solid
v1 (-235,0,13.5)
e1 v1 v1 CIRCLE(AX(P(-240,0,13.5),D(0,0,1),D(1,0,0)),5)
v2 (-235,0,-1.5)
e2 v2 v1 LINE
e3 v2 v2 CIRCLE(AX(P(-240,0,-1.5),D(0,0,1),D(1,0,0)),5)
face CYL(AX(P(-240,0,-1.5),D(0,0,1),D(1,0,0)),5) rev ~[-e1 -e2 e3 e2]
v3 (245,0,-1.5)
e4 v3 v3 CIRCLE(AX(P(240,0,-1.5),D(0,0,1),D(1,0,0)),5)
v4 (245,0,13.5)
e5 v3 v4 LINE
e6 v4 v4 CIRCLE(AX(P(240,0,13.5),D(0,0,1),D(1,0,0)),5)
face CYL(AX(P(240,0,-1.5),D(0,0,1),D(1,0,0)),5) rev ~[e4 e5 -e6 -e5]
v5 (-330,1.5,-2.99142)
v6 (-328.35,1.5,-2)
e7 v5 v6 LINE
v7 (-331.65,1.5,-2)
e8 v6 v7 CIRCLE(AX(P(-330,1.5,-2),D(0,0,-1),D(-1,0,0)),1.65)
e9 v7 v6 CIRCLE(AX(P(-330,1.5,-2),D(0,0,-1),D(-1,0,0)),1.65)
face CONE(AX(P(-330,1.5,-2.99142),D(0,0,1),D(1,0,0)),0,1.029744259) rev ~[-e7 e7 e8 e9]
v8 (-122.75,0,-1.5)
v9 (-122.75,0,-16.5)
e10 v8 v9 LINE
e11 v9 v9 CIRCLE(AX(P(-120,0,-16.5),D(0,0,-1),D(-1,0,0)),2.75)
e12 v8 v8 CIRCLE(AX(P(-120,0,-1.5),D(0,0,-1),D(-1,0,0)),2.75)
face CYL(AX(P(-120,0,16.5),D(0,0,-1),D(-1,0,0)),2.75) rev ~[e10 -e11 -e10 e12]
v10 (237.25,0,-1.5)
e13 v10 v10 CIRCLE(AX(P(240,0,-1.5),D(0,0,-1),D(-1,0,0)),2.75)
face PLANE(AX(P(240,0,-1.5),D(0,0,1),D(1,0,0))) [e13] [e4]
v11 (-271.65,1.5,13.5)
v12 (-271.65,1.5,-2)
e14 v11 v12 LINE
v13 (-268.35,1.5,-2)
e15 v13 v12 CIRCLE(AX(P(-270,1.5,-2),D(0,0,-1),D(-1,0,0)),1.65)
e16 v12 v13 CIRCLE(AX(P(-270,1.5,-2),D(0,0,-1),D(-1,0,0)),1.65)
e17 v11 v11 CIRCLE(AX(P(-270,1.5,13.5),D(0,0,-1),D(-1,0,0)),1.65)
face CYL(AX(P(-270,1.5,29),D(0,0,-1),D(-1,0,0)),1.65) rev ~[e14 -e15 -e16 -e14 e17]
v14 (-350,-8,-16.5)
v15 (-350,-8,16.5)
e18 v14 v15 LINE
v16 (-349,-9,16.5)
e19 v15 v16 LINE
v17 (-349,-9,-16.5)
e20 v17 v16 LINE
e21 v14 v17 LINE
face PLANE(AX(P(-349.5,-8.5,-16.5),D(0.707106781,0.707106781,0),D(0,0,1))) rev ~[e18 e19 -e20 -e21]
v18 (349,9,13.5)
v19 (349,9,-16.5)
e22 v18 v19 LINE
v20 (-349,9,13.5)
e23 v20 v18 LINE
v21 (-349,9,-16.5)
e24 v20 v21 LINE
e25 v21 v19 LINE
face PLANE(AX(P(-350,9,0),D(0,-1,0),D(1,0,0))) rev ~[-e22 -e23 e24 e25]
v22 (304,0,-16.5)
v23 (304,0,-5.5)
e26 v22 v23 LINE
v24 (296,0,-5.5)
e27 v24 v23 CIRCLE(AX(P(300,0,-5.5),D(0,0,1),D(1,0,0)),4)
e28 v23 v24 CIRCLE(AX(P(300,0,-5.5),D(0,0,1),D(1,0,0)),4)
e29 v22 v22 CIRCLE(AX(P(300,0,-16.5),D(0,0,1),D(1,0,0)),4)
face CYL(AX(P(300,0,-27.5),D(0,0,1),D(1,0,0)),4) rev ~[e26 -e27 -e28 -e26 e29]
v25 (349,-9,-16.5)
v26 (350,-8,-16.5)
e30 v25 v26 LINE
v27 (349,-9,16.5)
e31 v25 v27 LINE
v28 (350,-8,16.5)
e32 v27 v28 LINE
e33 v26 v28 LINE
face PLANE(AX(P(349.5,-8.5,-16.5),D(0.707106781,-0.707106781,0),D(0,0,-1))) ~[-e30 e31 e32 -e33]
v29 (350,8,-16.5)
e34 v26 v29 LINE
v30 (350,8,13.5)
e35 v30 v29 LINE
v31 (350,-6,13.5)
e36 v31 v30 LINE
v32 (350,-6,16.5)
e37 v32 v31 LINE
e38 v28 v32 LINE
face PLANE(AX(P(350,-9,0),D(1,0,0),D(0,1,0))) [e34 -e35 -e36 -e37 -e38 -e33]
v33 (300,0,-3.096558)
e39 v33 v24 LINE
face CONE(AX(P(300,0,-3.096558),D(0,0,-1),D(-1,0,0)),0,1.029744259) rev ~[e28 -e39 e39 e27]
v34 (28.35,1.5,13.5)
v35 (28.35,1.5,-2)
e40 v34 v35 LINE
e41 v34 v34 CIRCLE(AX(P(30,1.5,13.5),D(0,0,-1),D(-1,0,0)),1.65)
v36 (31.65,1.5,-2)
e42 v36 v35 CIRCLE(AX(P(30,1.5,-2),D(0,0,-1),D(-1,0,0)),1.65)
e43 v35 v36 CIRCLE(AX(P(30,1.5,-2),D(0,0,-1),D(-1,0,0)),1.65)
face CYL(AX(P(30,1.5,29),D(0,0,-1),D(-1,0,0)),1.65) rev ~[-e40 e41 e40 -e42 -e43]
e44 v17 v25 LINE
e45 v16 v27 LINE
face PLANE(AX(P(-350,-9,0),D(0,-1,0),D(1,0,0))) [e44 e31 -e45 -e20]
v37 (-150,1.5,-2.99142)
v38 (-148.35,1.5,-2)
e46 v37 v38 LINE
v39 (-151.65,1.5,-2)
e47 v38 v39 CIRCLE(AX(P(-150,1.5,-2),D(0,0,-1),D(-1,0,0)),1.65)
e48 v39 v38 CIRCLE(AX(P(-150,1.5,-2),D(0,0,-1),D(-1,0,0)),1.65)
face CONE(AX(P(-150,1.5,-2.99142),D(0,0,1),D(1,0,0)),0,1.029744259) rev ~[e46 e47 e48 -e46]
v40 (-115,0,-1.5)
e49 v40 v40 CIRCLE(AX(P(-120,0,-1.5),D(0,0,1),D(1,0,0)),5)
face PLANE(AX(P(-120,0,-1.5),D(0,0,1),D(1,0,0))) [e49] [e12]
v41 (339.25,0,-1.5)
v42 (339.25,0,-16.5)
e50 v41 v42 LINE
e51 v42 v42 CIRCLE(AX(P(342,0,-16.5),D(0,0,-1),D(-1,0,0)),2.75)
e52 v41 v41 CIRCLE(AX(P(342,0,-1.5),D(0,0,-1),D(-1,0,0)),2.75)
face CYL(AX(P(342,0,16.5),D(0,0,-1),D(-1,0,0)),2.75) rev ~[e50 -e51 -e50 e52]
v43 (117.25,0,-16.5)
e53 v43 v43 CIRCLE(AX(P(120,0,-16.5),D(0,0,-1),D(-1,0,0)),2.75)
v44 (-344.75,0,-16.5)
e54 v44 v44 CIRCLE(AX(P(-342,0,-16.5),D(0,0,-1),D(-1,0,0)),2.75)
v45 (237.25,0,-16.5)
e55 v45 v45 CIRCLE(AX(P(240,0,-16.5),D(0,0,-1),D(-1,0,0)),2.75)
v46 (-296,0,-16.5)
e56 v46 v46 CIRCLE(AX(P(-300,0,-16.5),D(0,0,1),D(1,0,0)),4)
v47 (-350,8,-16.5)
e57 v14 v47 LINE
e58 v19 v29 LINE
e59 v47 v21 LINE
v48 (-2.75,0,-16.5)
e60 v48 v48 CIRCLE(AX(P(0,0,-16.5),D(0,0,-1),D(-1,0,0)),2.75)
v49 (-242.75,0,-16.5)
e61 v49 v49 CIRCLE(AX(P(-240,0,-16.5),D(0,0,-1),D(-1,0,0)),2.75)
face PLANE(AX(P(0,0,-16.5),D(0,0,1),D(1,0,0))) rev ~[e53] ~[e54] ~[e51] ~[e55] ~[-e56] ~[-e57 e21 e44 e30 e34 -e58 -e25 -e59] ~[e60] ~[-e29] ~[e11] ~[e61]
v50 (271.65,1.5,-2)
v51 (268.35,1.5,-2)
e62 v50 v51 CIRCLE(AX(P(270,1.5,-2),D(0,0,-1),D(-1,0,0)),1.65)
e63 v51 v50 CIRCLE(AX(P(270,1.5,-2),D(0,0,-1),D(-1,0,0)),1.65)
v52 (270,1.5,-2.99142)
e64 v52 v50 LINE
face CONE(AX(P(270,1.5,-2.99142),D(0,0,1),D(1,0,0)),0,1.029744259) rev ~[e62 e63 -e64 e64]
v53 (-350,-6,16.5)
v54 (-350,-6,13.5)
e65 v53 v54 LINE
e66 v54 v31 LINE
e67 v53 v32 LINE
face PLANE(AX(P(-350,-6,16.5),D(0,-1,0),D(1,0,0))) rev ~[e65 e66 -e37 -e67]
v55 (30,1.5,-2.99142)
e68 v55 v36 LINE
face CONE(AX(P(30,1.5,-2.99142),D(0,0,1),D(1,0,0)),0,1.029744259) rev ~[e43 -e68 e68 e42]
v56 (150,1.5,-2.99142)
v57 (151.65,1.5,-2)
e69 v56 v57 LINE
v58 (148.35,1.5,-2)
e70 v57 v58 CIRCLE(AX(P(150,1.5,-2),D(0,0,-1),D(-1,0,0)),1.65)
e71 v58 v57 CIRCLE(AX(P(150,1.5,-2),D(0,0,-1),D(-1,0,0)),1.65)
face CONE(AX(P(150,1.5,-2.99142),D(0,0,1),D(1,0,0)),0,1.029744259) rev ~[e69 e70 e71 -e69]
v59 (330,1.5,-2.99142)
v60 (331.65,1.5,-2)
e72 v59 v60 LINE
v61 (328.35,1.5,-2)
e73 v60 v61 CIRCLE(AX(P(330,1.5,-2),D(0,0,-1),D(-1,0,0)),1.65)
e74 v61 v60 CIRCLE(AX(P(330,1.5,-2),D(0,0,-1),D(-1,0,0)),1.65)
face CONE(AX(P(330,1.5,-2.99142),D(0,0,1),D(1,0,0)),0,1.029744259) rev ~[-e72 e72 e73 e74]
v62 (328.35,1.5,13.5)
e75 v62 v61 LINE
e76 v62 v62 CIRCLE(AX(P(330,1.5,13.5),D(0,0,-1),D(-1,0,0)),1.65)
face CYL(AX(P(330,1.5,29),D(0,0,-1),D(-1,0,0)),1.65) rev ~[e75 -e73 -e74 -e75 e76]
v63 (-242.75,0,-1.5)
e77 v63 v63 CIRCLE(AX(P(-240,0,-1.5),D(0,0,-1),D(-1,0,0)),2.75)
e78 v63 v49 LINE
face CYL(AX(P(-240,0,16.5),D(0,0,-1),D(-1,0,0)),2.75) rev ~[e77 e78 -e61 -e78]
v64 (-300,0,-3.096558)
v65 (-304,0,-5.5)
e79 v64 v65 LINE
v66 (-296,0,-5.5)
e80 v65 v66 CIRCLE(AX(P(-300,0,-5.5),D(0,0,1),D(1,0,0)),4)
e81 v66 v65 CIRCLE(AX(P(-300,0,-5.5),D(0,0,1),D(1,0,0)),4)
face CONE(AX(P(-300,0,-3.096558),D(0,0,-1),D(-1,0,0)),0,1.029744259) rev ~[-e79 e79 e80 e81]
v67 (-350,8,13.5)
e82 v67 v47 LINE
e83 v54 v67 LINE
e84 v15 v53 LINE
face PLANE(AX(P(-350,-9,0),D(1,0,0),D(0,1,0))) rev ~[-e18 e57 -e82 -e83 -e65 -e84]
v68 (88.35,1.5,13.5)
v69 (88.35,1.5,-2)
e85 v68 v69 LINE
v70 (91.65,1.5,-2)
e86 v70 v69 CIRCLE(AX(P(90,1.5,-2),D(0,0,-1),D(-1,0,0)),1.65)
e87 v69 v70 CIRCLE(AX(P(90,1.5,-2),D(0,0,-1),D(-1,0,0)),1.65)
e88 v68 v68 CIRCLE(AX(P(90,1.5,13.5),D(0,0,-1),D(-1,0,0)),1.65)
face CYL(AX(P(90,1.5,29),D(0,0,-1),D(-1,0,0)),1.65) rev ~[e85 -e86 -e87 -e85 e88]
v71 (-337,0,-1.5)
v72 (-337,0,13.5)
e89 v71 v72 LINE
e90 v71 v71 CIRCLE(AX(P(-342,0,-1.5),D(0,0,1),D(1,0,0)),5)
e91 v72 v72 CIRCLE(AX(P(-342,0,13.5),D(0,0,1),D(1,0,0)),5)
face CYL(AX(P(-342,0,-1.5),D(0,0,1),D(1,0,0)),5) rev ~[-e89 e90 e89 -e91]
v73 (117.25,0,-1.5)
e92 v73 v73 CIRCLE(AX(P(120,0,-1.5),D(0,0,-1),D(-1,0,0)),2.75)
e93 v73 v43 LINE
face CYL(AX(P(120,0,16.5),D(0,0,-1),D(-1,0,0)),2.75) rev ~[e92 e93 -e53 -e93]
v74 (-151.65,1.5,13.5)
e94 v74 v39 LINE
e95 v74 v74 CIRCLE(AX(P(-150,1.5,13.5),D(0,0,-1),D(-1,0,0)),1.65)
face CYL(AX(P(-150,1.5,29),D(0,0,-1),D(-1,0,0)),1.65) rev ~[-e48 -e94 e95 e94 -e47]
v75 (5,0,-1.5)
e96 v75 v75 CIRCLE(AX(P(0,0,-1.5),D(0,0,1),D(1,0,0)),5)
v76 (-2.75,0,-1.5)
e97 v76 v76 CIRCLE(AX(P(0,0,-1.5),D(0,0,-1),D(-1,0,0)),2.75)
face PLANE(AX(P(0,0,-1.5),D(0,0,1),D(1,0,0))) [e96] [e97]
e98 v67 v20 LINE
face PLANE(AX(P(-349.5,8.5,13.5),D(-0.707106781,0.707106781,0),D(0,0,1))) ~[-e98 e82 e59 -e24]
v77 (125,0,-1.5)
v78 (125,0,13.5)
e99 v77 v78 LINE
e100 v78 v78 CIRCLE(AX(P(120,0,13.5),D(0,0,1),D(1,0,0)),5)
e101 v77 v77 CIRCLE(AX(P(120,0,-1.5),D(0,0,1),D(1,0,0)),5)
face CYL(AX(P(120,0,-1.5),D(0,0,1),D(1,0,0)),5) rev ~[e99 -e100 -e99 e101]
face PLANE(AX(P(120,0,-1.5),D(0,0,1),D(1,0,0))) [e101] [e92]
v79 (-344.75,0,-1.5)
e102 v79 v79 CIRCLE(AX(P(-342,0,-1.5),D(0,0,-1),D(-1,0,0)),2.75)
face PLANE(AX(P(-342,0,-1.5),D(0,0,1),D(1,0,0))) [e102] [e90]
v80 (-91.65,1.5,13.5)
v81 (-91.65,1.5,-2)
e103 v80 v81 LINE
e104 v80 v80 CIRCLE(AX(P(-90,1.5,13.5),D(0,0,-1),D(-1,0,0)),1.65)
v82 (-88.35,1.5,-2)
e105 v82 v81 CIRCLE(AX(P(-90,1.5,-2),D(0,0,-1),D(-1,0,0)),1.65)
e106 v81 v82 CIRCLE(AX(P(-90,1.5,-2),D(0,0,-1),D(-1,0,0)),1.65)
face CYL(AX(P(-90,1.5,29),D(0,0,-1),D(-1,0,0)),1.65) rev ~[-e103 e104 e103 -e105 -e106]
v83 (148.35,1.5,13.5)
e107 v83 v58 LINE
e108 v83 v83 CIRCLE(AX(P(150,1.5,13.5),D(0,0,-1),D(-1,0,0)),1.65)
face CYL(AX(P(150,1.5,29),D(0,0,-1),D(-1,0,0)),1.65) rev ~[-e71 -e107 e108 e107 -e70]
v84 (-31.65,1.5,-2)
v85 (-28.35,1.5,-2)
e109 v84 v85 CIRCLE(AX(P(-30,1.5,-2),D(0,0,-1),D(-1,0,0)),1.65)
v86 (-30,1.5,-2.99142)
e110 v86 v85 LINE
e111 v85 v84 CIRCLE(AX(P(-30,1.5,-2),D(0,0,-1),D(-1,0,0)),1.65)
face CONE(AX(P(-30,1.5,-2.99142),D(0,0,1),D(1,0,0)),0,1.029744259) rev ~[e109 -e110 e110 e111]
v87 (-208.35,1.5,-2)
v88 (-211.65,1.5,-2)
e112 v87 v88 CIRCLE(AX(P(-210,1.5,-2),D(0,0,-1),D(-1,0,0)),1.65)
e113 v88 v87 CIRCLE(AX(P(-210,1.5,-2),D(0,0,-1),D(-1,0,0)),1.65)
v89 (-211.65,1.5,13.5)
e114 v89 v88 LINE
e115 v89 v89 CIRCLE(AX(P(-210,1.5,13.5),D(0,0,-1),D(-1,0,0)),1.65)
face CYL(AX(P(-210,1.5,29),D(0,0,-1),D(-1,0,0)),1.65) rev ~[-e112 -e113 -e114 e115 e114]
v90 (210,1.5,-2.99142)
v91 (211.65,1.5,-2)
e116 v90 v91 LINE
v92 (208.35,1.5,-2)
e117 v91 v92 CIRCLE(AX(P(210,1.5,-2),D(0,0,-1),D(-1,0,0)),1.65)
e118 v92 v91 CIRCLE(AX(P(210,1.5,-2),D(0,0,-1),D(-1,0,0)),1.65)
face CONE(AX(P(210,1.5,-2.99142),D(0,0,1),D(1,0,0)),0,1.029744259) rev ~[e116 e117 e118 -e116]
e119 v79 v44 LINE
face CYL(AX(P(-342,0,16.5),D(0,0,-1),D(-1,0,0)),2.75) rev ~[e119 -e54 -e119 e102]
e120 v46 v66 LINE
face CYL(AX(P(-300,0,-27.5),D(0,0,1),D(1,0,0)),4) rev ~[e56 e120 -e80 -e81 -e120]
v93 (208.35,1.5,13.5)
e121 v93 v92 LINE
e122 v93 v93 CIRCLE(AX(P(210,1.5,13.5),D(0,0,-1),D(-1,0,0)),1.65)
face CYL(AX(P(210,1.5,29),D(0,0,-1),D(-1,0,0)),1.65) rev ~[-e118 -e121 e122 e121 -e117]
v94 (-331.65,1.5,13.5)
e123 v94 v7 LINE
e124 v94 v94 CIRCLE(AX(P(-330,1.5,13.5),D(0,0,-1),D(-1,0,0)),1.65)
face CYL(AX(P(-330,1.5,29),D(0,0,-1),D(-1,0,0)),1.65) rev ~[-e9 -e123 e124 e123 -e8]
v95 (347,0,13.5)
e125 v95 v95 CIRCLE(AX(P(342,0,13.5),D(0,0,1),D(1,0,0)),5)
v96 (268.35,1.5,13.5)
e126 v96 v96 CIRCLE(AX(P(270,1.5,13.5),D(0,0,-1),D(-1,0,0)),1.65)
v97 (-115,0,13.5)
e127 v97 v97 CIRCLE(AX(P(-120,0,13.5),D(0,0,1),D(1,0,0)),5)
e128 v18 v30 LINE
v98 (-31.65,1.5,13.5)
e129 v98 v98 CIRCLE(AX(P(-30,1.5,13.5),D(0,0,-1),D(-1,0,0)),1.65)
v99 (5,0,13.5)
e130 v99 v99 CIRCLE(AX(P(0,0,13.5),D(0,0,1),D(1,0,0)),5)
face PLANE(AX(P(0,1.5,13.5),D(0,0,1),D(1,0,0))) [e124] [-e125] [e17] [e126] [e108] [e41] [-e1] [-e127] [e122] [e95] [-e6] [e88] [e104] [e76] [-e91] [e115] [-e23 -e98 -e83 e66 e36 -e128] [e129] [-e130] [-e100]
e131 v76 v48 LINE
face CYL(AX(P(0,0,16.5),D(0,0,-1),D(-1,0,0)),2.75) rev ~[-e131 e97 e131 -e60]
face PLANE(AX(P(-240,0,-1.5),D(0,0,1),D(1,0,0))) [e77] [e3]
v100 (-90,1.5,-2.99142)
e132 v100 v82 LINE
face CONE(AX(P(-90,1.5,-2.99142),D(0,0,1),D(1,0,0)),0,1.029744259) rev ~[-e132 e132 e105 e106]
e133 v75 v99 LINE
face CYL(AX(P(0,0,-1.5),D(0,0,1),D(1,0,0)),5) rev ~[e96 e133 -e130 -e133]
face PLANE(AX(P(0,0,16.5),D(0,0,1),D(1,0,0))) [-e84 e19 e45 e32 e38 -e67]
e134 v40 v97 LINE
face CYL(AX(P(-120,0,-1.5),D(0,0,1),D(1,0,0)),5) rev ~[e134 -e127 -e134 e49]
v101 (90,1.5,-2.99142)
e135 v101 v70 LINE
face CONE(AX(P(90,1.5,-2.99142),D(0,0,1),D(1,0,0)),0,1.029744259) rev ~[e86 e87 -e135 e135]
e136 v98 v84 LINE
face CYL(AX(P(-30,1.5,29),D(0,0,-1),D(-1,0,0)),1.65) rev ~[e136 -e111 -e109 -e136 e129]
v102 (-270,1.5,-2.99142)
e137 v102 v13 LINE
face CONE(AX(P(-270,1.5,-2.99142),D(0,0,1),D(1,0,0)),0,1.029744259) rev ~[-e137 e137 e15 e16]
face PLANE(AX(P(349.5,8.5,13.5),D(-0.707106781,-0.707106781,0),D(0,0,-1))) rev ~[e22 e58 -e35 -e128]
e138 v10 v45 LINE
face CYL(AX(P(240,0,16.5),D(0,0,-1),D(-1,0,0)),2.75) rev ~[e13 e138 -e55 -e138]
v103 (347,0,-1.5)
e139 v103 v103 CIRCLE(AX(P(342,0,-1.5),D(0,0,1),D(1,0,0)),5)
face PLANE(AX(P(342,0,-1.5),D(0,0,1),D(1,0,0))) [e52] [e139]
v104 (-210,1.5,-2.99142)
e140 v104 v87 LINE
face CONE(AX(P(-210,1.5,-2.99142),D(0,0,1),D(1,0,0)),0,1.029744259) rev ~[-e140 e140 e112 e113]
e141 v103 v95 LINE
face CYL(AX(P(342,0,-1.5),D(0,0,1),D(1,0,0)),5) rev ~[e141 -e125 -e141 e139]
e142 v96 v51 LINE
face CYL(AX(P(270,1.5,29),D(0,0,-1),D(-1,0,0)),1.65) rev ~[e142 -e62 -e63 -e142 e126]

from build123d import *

# Parameters (mm, degrees)
SKETCH1_W                                           = 700
SKETCH1_H                                           = 18
BOSS_EXTRUDE1_DEPTH                                 = 16.5
SKETCH4_W                                           = 700
SKETCH4_H                                           = 15
CUT_EXTRUDE1_DEPTH                                  = 3
M4_TAPPED_HOLE1_D                                   = 3.3
M4_TAPPED_HOLE1_DEPTH                               = 15.5
M4_TAPPED_HOLE1_TIP                                 = 0.991420021
CBORE_FOR_M5_HEX_SOCKET_HEAD_CAP_SCREW1_D           = 5.5
CBORE_FOR_M5_HEX_SOCKET_HEAD_CAP_SCREW1_CBORE_D     = 10
CBORE_FOR_M5_HEX_SOCKET_HEAD_CAP_SCREW1_CBORE_DEPTH = 18
SIZE_MM_DOWEL_HOLE_1_D                              = 8
SIZE_MM_DOWEL_HOLE_1_DEPTH                          = 11
SIZE_MM_DOWEL_HOLE_1_TIP                            = 2.403442476
CHAMFER1_SIZE                                       = 1


with BuildPart() as part:
    # Sketch1 → Boss-Extrude1 (new, symmetric)
    with BuildSketch(Plane.XY):
        Rectangle(SKETCH1_W, SKETCH1_H)
    extrude(amount=BOSS_EXTRUDE1_DEPTH, both=True)

    # Sketch4 → Cut-Extrude1 (cut)
    with BuildSketch(Plane.XY.offset(16.5)):
        with Locations((0, 1.5)):
            Rectangle(SKETCH4_W, SKETCH4_H)
    extrude(amount=-CUT_EXTRUDE1_DEPTH, mode=Mode.SUBTRACT)

    # M4 Tapped Hole1
    with Locations(Plane.XY.offset(13.5)):
        with Locations((330, 1.5), (270, 1.5), (210, 1.5), (150, 1.5), (90, 1.5), (30, 1.5), (-30, 1.5), (-90, 1.5), (-150, 1.5), (-330, 1.5), (-210, 1.5), (-270, 1.5)):
            Hole(M4_TAPPED_HOLE1_D / 2, depth=M4_TAPPED_HOLE1_DEPTH)
            with Locations((0, 0, -(M4_TAPPED_HOLE1_DEPTH + M4_TAPPED_HOLE1_TIP / 2))):  # 118° drill point
                Cone(0, M4_TAPPED_HOLE1_D / 2, M4_TAPPED_HOLE1_TIP, mode=Mode.SUBTRACT)

    # CBORE for M5 Hex Socket Head Cap Screw1 (through all)
    with Locations(Plane.XY.offset(16.5)):
        with Locations((-342, 0), (-240, 0), (-120, 0), (0, 0), (120, 0), (240, 0), (342, 0)):
            CounterBoreHole(CBORE_FOR_M5_HEX_SOCKET_HEAD_CAP_SCREW1_D / 2, CBORE_FOR_M5_HEX_SOCKET_HEAD_CAP_SCREW1_CBORE_D / 2, CBORE_FOR_M5_HEX_SOCKET_HEAD_CAP_SCREW1_CBORE_DEPTH)

    # Size mm dowel hole 1
    with Locations(Plane(origin=(0, 0, -16.5), x_dir=(-1, 0, 0), z_dir=(0, 0, -1))):
        with Locations((-300, 0), (300, 0)):
            Hole(SIZE_MM_DOWEL_HOLE_1_D / 2, depth=SIZE_MM_DOWEL_HOLE_1_DEPTH)
            with Locations((0, 0, -(SIZE_MM_DOWEL_HOLE_1_DEPTH + SIZE_MM_DOWEL_HOLE_1_TIP / 2))):  # 118° drill point
                Cone(0, SIZE_MM_DOWEL_HOLE_1_D / 2, SIZE_MM_DOWEL_HOLE_1_TIP, mode=Mode.SUBTRACT)

    # Chamfer1
    chamfer1_edges = [part.edges().sort_by_distance(p)[0] for p in [
        (-350, 9, -1.5),
        (350, 9, -1.5),
        (350, -9, 0),
        (-350, -9, 0),
    ]]
    chamfer(chamfer1_edges, length=CHAMFER1_SIZE)


solid = part.part
